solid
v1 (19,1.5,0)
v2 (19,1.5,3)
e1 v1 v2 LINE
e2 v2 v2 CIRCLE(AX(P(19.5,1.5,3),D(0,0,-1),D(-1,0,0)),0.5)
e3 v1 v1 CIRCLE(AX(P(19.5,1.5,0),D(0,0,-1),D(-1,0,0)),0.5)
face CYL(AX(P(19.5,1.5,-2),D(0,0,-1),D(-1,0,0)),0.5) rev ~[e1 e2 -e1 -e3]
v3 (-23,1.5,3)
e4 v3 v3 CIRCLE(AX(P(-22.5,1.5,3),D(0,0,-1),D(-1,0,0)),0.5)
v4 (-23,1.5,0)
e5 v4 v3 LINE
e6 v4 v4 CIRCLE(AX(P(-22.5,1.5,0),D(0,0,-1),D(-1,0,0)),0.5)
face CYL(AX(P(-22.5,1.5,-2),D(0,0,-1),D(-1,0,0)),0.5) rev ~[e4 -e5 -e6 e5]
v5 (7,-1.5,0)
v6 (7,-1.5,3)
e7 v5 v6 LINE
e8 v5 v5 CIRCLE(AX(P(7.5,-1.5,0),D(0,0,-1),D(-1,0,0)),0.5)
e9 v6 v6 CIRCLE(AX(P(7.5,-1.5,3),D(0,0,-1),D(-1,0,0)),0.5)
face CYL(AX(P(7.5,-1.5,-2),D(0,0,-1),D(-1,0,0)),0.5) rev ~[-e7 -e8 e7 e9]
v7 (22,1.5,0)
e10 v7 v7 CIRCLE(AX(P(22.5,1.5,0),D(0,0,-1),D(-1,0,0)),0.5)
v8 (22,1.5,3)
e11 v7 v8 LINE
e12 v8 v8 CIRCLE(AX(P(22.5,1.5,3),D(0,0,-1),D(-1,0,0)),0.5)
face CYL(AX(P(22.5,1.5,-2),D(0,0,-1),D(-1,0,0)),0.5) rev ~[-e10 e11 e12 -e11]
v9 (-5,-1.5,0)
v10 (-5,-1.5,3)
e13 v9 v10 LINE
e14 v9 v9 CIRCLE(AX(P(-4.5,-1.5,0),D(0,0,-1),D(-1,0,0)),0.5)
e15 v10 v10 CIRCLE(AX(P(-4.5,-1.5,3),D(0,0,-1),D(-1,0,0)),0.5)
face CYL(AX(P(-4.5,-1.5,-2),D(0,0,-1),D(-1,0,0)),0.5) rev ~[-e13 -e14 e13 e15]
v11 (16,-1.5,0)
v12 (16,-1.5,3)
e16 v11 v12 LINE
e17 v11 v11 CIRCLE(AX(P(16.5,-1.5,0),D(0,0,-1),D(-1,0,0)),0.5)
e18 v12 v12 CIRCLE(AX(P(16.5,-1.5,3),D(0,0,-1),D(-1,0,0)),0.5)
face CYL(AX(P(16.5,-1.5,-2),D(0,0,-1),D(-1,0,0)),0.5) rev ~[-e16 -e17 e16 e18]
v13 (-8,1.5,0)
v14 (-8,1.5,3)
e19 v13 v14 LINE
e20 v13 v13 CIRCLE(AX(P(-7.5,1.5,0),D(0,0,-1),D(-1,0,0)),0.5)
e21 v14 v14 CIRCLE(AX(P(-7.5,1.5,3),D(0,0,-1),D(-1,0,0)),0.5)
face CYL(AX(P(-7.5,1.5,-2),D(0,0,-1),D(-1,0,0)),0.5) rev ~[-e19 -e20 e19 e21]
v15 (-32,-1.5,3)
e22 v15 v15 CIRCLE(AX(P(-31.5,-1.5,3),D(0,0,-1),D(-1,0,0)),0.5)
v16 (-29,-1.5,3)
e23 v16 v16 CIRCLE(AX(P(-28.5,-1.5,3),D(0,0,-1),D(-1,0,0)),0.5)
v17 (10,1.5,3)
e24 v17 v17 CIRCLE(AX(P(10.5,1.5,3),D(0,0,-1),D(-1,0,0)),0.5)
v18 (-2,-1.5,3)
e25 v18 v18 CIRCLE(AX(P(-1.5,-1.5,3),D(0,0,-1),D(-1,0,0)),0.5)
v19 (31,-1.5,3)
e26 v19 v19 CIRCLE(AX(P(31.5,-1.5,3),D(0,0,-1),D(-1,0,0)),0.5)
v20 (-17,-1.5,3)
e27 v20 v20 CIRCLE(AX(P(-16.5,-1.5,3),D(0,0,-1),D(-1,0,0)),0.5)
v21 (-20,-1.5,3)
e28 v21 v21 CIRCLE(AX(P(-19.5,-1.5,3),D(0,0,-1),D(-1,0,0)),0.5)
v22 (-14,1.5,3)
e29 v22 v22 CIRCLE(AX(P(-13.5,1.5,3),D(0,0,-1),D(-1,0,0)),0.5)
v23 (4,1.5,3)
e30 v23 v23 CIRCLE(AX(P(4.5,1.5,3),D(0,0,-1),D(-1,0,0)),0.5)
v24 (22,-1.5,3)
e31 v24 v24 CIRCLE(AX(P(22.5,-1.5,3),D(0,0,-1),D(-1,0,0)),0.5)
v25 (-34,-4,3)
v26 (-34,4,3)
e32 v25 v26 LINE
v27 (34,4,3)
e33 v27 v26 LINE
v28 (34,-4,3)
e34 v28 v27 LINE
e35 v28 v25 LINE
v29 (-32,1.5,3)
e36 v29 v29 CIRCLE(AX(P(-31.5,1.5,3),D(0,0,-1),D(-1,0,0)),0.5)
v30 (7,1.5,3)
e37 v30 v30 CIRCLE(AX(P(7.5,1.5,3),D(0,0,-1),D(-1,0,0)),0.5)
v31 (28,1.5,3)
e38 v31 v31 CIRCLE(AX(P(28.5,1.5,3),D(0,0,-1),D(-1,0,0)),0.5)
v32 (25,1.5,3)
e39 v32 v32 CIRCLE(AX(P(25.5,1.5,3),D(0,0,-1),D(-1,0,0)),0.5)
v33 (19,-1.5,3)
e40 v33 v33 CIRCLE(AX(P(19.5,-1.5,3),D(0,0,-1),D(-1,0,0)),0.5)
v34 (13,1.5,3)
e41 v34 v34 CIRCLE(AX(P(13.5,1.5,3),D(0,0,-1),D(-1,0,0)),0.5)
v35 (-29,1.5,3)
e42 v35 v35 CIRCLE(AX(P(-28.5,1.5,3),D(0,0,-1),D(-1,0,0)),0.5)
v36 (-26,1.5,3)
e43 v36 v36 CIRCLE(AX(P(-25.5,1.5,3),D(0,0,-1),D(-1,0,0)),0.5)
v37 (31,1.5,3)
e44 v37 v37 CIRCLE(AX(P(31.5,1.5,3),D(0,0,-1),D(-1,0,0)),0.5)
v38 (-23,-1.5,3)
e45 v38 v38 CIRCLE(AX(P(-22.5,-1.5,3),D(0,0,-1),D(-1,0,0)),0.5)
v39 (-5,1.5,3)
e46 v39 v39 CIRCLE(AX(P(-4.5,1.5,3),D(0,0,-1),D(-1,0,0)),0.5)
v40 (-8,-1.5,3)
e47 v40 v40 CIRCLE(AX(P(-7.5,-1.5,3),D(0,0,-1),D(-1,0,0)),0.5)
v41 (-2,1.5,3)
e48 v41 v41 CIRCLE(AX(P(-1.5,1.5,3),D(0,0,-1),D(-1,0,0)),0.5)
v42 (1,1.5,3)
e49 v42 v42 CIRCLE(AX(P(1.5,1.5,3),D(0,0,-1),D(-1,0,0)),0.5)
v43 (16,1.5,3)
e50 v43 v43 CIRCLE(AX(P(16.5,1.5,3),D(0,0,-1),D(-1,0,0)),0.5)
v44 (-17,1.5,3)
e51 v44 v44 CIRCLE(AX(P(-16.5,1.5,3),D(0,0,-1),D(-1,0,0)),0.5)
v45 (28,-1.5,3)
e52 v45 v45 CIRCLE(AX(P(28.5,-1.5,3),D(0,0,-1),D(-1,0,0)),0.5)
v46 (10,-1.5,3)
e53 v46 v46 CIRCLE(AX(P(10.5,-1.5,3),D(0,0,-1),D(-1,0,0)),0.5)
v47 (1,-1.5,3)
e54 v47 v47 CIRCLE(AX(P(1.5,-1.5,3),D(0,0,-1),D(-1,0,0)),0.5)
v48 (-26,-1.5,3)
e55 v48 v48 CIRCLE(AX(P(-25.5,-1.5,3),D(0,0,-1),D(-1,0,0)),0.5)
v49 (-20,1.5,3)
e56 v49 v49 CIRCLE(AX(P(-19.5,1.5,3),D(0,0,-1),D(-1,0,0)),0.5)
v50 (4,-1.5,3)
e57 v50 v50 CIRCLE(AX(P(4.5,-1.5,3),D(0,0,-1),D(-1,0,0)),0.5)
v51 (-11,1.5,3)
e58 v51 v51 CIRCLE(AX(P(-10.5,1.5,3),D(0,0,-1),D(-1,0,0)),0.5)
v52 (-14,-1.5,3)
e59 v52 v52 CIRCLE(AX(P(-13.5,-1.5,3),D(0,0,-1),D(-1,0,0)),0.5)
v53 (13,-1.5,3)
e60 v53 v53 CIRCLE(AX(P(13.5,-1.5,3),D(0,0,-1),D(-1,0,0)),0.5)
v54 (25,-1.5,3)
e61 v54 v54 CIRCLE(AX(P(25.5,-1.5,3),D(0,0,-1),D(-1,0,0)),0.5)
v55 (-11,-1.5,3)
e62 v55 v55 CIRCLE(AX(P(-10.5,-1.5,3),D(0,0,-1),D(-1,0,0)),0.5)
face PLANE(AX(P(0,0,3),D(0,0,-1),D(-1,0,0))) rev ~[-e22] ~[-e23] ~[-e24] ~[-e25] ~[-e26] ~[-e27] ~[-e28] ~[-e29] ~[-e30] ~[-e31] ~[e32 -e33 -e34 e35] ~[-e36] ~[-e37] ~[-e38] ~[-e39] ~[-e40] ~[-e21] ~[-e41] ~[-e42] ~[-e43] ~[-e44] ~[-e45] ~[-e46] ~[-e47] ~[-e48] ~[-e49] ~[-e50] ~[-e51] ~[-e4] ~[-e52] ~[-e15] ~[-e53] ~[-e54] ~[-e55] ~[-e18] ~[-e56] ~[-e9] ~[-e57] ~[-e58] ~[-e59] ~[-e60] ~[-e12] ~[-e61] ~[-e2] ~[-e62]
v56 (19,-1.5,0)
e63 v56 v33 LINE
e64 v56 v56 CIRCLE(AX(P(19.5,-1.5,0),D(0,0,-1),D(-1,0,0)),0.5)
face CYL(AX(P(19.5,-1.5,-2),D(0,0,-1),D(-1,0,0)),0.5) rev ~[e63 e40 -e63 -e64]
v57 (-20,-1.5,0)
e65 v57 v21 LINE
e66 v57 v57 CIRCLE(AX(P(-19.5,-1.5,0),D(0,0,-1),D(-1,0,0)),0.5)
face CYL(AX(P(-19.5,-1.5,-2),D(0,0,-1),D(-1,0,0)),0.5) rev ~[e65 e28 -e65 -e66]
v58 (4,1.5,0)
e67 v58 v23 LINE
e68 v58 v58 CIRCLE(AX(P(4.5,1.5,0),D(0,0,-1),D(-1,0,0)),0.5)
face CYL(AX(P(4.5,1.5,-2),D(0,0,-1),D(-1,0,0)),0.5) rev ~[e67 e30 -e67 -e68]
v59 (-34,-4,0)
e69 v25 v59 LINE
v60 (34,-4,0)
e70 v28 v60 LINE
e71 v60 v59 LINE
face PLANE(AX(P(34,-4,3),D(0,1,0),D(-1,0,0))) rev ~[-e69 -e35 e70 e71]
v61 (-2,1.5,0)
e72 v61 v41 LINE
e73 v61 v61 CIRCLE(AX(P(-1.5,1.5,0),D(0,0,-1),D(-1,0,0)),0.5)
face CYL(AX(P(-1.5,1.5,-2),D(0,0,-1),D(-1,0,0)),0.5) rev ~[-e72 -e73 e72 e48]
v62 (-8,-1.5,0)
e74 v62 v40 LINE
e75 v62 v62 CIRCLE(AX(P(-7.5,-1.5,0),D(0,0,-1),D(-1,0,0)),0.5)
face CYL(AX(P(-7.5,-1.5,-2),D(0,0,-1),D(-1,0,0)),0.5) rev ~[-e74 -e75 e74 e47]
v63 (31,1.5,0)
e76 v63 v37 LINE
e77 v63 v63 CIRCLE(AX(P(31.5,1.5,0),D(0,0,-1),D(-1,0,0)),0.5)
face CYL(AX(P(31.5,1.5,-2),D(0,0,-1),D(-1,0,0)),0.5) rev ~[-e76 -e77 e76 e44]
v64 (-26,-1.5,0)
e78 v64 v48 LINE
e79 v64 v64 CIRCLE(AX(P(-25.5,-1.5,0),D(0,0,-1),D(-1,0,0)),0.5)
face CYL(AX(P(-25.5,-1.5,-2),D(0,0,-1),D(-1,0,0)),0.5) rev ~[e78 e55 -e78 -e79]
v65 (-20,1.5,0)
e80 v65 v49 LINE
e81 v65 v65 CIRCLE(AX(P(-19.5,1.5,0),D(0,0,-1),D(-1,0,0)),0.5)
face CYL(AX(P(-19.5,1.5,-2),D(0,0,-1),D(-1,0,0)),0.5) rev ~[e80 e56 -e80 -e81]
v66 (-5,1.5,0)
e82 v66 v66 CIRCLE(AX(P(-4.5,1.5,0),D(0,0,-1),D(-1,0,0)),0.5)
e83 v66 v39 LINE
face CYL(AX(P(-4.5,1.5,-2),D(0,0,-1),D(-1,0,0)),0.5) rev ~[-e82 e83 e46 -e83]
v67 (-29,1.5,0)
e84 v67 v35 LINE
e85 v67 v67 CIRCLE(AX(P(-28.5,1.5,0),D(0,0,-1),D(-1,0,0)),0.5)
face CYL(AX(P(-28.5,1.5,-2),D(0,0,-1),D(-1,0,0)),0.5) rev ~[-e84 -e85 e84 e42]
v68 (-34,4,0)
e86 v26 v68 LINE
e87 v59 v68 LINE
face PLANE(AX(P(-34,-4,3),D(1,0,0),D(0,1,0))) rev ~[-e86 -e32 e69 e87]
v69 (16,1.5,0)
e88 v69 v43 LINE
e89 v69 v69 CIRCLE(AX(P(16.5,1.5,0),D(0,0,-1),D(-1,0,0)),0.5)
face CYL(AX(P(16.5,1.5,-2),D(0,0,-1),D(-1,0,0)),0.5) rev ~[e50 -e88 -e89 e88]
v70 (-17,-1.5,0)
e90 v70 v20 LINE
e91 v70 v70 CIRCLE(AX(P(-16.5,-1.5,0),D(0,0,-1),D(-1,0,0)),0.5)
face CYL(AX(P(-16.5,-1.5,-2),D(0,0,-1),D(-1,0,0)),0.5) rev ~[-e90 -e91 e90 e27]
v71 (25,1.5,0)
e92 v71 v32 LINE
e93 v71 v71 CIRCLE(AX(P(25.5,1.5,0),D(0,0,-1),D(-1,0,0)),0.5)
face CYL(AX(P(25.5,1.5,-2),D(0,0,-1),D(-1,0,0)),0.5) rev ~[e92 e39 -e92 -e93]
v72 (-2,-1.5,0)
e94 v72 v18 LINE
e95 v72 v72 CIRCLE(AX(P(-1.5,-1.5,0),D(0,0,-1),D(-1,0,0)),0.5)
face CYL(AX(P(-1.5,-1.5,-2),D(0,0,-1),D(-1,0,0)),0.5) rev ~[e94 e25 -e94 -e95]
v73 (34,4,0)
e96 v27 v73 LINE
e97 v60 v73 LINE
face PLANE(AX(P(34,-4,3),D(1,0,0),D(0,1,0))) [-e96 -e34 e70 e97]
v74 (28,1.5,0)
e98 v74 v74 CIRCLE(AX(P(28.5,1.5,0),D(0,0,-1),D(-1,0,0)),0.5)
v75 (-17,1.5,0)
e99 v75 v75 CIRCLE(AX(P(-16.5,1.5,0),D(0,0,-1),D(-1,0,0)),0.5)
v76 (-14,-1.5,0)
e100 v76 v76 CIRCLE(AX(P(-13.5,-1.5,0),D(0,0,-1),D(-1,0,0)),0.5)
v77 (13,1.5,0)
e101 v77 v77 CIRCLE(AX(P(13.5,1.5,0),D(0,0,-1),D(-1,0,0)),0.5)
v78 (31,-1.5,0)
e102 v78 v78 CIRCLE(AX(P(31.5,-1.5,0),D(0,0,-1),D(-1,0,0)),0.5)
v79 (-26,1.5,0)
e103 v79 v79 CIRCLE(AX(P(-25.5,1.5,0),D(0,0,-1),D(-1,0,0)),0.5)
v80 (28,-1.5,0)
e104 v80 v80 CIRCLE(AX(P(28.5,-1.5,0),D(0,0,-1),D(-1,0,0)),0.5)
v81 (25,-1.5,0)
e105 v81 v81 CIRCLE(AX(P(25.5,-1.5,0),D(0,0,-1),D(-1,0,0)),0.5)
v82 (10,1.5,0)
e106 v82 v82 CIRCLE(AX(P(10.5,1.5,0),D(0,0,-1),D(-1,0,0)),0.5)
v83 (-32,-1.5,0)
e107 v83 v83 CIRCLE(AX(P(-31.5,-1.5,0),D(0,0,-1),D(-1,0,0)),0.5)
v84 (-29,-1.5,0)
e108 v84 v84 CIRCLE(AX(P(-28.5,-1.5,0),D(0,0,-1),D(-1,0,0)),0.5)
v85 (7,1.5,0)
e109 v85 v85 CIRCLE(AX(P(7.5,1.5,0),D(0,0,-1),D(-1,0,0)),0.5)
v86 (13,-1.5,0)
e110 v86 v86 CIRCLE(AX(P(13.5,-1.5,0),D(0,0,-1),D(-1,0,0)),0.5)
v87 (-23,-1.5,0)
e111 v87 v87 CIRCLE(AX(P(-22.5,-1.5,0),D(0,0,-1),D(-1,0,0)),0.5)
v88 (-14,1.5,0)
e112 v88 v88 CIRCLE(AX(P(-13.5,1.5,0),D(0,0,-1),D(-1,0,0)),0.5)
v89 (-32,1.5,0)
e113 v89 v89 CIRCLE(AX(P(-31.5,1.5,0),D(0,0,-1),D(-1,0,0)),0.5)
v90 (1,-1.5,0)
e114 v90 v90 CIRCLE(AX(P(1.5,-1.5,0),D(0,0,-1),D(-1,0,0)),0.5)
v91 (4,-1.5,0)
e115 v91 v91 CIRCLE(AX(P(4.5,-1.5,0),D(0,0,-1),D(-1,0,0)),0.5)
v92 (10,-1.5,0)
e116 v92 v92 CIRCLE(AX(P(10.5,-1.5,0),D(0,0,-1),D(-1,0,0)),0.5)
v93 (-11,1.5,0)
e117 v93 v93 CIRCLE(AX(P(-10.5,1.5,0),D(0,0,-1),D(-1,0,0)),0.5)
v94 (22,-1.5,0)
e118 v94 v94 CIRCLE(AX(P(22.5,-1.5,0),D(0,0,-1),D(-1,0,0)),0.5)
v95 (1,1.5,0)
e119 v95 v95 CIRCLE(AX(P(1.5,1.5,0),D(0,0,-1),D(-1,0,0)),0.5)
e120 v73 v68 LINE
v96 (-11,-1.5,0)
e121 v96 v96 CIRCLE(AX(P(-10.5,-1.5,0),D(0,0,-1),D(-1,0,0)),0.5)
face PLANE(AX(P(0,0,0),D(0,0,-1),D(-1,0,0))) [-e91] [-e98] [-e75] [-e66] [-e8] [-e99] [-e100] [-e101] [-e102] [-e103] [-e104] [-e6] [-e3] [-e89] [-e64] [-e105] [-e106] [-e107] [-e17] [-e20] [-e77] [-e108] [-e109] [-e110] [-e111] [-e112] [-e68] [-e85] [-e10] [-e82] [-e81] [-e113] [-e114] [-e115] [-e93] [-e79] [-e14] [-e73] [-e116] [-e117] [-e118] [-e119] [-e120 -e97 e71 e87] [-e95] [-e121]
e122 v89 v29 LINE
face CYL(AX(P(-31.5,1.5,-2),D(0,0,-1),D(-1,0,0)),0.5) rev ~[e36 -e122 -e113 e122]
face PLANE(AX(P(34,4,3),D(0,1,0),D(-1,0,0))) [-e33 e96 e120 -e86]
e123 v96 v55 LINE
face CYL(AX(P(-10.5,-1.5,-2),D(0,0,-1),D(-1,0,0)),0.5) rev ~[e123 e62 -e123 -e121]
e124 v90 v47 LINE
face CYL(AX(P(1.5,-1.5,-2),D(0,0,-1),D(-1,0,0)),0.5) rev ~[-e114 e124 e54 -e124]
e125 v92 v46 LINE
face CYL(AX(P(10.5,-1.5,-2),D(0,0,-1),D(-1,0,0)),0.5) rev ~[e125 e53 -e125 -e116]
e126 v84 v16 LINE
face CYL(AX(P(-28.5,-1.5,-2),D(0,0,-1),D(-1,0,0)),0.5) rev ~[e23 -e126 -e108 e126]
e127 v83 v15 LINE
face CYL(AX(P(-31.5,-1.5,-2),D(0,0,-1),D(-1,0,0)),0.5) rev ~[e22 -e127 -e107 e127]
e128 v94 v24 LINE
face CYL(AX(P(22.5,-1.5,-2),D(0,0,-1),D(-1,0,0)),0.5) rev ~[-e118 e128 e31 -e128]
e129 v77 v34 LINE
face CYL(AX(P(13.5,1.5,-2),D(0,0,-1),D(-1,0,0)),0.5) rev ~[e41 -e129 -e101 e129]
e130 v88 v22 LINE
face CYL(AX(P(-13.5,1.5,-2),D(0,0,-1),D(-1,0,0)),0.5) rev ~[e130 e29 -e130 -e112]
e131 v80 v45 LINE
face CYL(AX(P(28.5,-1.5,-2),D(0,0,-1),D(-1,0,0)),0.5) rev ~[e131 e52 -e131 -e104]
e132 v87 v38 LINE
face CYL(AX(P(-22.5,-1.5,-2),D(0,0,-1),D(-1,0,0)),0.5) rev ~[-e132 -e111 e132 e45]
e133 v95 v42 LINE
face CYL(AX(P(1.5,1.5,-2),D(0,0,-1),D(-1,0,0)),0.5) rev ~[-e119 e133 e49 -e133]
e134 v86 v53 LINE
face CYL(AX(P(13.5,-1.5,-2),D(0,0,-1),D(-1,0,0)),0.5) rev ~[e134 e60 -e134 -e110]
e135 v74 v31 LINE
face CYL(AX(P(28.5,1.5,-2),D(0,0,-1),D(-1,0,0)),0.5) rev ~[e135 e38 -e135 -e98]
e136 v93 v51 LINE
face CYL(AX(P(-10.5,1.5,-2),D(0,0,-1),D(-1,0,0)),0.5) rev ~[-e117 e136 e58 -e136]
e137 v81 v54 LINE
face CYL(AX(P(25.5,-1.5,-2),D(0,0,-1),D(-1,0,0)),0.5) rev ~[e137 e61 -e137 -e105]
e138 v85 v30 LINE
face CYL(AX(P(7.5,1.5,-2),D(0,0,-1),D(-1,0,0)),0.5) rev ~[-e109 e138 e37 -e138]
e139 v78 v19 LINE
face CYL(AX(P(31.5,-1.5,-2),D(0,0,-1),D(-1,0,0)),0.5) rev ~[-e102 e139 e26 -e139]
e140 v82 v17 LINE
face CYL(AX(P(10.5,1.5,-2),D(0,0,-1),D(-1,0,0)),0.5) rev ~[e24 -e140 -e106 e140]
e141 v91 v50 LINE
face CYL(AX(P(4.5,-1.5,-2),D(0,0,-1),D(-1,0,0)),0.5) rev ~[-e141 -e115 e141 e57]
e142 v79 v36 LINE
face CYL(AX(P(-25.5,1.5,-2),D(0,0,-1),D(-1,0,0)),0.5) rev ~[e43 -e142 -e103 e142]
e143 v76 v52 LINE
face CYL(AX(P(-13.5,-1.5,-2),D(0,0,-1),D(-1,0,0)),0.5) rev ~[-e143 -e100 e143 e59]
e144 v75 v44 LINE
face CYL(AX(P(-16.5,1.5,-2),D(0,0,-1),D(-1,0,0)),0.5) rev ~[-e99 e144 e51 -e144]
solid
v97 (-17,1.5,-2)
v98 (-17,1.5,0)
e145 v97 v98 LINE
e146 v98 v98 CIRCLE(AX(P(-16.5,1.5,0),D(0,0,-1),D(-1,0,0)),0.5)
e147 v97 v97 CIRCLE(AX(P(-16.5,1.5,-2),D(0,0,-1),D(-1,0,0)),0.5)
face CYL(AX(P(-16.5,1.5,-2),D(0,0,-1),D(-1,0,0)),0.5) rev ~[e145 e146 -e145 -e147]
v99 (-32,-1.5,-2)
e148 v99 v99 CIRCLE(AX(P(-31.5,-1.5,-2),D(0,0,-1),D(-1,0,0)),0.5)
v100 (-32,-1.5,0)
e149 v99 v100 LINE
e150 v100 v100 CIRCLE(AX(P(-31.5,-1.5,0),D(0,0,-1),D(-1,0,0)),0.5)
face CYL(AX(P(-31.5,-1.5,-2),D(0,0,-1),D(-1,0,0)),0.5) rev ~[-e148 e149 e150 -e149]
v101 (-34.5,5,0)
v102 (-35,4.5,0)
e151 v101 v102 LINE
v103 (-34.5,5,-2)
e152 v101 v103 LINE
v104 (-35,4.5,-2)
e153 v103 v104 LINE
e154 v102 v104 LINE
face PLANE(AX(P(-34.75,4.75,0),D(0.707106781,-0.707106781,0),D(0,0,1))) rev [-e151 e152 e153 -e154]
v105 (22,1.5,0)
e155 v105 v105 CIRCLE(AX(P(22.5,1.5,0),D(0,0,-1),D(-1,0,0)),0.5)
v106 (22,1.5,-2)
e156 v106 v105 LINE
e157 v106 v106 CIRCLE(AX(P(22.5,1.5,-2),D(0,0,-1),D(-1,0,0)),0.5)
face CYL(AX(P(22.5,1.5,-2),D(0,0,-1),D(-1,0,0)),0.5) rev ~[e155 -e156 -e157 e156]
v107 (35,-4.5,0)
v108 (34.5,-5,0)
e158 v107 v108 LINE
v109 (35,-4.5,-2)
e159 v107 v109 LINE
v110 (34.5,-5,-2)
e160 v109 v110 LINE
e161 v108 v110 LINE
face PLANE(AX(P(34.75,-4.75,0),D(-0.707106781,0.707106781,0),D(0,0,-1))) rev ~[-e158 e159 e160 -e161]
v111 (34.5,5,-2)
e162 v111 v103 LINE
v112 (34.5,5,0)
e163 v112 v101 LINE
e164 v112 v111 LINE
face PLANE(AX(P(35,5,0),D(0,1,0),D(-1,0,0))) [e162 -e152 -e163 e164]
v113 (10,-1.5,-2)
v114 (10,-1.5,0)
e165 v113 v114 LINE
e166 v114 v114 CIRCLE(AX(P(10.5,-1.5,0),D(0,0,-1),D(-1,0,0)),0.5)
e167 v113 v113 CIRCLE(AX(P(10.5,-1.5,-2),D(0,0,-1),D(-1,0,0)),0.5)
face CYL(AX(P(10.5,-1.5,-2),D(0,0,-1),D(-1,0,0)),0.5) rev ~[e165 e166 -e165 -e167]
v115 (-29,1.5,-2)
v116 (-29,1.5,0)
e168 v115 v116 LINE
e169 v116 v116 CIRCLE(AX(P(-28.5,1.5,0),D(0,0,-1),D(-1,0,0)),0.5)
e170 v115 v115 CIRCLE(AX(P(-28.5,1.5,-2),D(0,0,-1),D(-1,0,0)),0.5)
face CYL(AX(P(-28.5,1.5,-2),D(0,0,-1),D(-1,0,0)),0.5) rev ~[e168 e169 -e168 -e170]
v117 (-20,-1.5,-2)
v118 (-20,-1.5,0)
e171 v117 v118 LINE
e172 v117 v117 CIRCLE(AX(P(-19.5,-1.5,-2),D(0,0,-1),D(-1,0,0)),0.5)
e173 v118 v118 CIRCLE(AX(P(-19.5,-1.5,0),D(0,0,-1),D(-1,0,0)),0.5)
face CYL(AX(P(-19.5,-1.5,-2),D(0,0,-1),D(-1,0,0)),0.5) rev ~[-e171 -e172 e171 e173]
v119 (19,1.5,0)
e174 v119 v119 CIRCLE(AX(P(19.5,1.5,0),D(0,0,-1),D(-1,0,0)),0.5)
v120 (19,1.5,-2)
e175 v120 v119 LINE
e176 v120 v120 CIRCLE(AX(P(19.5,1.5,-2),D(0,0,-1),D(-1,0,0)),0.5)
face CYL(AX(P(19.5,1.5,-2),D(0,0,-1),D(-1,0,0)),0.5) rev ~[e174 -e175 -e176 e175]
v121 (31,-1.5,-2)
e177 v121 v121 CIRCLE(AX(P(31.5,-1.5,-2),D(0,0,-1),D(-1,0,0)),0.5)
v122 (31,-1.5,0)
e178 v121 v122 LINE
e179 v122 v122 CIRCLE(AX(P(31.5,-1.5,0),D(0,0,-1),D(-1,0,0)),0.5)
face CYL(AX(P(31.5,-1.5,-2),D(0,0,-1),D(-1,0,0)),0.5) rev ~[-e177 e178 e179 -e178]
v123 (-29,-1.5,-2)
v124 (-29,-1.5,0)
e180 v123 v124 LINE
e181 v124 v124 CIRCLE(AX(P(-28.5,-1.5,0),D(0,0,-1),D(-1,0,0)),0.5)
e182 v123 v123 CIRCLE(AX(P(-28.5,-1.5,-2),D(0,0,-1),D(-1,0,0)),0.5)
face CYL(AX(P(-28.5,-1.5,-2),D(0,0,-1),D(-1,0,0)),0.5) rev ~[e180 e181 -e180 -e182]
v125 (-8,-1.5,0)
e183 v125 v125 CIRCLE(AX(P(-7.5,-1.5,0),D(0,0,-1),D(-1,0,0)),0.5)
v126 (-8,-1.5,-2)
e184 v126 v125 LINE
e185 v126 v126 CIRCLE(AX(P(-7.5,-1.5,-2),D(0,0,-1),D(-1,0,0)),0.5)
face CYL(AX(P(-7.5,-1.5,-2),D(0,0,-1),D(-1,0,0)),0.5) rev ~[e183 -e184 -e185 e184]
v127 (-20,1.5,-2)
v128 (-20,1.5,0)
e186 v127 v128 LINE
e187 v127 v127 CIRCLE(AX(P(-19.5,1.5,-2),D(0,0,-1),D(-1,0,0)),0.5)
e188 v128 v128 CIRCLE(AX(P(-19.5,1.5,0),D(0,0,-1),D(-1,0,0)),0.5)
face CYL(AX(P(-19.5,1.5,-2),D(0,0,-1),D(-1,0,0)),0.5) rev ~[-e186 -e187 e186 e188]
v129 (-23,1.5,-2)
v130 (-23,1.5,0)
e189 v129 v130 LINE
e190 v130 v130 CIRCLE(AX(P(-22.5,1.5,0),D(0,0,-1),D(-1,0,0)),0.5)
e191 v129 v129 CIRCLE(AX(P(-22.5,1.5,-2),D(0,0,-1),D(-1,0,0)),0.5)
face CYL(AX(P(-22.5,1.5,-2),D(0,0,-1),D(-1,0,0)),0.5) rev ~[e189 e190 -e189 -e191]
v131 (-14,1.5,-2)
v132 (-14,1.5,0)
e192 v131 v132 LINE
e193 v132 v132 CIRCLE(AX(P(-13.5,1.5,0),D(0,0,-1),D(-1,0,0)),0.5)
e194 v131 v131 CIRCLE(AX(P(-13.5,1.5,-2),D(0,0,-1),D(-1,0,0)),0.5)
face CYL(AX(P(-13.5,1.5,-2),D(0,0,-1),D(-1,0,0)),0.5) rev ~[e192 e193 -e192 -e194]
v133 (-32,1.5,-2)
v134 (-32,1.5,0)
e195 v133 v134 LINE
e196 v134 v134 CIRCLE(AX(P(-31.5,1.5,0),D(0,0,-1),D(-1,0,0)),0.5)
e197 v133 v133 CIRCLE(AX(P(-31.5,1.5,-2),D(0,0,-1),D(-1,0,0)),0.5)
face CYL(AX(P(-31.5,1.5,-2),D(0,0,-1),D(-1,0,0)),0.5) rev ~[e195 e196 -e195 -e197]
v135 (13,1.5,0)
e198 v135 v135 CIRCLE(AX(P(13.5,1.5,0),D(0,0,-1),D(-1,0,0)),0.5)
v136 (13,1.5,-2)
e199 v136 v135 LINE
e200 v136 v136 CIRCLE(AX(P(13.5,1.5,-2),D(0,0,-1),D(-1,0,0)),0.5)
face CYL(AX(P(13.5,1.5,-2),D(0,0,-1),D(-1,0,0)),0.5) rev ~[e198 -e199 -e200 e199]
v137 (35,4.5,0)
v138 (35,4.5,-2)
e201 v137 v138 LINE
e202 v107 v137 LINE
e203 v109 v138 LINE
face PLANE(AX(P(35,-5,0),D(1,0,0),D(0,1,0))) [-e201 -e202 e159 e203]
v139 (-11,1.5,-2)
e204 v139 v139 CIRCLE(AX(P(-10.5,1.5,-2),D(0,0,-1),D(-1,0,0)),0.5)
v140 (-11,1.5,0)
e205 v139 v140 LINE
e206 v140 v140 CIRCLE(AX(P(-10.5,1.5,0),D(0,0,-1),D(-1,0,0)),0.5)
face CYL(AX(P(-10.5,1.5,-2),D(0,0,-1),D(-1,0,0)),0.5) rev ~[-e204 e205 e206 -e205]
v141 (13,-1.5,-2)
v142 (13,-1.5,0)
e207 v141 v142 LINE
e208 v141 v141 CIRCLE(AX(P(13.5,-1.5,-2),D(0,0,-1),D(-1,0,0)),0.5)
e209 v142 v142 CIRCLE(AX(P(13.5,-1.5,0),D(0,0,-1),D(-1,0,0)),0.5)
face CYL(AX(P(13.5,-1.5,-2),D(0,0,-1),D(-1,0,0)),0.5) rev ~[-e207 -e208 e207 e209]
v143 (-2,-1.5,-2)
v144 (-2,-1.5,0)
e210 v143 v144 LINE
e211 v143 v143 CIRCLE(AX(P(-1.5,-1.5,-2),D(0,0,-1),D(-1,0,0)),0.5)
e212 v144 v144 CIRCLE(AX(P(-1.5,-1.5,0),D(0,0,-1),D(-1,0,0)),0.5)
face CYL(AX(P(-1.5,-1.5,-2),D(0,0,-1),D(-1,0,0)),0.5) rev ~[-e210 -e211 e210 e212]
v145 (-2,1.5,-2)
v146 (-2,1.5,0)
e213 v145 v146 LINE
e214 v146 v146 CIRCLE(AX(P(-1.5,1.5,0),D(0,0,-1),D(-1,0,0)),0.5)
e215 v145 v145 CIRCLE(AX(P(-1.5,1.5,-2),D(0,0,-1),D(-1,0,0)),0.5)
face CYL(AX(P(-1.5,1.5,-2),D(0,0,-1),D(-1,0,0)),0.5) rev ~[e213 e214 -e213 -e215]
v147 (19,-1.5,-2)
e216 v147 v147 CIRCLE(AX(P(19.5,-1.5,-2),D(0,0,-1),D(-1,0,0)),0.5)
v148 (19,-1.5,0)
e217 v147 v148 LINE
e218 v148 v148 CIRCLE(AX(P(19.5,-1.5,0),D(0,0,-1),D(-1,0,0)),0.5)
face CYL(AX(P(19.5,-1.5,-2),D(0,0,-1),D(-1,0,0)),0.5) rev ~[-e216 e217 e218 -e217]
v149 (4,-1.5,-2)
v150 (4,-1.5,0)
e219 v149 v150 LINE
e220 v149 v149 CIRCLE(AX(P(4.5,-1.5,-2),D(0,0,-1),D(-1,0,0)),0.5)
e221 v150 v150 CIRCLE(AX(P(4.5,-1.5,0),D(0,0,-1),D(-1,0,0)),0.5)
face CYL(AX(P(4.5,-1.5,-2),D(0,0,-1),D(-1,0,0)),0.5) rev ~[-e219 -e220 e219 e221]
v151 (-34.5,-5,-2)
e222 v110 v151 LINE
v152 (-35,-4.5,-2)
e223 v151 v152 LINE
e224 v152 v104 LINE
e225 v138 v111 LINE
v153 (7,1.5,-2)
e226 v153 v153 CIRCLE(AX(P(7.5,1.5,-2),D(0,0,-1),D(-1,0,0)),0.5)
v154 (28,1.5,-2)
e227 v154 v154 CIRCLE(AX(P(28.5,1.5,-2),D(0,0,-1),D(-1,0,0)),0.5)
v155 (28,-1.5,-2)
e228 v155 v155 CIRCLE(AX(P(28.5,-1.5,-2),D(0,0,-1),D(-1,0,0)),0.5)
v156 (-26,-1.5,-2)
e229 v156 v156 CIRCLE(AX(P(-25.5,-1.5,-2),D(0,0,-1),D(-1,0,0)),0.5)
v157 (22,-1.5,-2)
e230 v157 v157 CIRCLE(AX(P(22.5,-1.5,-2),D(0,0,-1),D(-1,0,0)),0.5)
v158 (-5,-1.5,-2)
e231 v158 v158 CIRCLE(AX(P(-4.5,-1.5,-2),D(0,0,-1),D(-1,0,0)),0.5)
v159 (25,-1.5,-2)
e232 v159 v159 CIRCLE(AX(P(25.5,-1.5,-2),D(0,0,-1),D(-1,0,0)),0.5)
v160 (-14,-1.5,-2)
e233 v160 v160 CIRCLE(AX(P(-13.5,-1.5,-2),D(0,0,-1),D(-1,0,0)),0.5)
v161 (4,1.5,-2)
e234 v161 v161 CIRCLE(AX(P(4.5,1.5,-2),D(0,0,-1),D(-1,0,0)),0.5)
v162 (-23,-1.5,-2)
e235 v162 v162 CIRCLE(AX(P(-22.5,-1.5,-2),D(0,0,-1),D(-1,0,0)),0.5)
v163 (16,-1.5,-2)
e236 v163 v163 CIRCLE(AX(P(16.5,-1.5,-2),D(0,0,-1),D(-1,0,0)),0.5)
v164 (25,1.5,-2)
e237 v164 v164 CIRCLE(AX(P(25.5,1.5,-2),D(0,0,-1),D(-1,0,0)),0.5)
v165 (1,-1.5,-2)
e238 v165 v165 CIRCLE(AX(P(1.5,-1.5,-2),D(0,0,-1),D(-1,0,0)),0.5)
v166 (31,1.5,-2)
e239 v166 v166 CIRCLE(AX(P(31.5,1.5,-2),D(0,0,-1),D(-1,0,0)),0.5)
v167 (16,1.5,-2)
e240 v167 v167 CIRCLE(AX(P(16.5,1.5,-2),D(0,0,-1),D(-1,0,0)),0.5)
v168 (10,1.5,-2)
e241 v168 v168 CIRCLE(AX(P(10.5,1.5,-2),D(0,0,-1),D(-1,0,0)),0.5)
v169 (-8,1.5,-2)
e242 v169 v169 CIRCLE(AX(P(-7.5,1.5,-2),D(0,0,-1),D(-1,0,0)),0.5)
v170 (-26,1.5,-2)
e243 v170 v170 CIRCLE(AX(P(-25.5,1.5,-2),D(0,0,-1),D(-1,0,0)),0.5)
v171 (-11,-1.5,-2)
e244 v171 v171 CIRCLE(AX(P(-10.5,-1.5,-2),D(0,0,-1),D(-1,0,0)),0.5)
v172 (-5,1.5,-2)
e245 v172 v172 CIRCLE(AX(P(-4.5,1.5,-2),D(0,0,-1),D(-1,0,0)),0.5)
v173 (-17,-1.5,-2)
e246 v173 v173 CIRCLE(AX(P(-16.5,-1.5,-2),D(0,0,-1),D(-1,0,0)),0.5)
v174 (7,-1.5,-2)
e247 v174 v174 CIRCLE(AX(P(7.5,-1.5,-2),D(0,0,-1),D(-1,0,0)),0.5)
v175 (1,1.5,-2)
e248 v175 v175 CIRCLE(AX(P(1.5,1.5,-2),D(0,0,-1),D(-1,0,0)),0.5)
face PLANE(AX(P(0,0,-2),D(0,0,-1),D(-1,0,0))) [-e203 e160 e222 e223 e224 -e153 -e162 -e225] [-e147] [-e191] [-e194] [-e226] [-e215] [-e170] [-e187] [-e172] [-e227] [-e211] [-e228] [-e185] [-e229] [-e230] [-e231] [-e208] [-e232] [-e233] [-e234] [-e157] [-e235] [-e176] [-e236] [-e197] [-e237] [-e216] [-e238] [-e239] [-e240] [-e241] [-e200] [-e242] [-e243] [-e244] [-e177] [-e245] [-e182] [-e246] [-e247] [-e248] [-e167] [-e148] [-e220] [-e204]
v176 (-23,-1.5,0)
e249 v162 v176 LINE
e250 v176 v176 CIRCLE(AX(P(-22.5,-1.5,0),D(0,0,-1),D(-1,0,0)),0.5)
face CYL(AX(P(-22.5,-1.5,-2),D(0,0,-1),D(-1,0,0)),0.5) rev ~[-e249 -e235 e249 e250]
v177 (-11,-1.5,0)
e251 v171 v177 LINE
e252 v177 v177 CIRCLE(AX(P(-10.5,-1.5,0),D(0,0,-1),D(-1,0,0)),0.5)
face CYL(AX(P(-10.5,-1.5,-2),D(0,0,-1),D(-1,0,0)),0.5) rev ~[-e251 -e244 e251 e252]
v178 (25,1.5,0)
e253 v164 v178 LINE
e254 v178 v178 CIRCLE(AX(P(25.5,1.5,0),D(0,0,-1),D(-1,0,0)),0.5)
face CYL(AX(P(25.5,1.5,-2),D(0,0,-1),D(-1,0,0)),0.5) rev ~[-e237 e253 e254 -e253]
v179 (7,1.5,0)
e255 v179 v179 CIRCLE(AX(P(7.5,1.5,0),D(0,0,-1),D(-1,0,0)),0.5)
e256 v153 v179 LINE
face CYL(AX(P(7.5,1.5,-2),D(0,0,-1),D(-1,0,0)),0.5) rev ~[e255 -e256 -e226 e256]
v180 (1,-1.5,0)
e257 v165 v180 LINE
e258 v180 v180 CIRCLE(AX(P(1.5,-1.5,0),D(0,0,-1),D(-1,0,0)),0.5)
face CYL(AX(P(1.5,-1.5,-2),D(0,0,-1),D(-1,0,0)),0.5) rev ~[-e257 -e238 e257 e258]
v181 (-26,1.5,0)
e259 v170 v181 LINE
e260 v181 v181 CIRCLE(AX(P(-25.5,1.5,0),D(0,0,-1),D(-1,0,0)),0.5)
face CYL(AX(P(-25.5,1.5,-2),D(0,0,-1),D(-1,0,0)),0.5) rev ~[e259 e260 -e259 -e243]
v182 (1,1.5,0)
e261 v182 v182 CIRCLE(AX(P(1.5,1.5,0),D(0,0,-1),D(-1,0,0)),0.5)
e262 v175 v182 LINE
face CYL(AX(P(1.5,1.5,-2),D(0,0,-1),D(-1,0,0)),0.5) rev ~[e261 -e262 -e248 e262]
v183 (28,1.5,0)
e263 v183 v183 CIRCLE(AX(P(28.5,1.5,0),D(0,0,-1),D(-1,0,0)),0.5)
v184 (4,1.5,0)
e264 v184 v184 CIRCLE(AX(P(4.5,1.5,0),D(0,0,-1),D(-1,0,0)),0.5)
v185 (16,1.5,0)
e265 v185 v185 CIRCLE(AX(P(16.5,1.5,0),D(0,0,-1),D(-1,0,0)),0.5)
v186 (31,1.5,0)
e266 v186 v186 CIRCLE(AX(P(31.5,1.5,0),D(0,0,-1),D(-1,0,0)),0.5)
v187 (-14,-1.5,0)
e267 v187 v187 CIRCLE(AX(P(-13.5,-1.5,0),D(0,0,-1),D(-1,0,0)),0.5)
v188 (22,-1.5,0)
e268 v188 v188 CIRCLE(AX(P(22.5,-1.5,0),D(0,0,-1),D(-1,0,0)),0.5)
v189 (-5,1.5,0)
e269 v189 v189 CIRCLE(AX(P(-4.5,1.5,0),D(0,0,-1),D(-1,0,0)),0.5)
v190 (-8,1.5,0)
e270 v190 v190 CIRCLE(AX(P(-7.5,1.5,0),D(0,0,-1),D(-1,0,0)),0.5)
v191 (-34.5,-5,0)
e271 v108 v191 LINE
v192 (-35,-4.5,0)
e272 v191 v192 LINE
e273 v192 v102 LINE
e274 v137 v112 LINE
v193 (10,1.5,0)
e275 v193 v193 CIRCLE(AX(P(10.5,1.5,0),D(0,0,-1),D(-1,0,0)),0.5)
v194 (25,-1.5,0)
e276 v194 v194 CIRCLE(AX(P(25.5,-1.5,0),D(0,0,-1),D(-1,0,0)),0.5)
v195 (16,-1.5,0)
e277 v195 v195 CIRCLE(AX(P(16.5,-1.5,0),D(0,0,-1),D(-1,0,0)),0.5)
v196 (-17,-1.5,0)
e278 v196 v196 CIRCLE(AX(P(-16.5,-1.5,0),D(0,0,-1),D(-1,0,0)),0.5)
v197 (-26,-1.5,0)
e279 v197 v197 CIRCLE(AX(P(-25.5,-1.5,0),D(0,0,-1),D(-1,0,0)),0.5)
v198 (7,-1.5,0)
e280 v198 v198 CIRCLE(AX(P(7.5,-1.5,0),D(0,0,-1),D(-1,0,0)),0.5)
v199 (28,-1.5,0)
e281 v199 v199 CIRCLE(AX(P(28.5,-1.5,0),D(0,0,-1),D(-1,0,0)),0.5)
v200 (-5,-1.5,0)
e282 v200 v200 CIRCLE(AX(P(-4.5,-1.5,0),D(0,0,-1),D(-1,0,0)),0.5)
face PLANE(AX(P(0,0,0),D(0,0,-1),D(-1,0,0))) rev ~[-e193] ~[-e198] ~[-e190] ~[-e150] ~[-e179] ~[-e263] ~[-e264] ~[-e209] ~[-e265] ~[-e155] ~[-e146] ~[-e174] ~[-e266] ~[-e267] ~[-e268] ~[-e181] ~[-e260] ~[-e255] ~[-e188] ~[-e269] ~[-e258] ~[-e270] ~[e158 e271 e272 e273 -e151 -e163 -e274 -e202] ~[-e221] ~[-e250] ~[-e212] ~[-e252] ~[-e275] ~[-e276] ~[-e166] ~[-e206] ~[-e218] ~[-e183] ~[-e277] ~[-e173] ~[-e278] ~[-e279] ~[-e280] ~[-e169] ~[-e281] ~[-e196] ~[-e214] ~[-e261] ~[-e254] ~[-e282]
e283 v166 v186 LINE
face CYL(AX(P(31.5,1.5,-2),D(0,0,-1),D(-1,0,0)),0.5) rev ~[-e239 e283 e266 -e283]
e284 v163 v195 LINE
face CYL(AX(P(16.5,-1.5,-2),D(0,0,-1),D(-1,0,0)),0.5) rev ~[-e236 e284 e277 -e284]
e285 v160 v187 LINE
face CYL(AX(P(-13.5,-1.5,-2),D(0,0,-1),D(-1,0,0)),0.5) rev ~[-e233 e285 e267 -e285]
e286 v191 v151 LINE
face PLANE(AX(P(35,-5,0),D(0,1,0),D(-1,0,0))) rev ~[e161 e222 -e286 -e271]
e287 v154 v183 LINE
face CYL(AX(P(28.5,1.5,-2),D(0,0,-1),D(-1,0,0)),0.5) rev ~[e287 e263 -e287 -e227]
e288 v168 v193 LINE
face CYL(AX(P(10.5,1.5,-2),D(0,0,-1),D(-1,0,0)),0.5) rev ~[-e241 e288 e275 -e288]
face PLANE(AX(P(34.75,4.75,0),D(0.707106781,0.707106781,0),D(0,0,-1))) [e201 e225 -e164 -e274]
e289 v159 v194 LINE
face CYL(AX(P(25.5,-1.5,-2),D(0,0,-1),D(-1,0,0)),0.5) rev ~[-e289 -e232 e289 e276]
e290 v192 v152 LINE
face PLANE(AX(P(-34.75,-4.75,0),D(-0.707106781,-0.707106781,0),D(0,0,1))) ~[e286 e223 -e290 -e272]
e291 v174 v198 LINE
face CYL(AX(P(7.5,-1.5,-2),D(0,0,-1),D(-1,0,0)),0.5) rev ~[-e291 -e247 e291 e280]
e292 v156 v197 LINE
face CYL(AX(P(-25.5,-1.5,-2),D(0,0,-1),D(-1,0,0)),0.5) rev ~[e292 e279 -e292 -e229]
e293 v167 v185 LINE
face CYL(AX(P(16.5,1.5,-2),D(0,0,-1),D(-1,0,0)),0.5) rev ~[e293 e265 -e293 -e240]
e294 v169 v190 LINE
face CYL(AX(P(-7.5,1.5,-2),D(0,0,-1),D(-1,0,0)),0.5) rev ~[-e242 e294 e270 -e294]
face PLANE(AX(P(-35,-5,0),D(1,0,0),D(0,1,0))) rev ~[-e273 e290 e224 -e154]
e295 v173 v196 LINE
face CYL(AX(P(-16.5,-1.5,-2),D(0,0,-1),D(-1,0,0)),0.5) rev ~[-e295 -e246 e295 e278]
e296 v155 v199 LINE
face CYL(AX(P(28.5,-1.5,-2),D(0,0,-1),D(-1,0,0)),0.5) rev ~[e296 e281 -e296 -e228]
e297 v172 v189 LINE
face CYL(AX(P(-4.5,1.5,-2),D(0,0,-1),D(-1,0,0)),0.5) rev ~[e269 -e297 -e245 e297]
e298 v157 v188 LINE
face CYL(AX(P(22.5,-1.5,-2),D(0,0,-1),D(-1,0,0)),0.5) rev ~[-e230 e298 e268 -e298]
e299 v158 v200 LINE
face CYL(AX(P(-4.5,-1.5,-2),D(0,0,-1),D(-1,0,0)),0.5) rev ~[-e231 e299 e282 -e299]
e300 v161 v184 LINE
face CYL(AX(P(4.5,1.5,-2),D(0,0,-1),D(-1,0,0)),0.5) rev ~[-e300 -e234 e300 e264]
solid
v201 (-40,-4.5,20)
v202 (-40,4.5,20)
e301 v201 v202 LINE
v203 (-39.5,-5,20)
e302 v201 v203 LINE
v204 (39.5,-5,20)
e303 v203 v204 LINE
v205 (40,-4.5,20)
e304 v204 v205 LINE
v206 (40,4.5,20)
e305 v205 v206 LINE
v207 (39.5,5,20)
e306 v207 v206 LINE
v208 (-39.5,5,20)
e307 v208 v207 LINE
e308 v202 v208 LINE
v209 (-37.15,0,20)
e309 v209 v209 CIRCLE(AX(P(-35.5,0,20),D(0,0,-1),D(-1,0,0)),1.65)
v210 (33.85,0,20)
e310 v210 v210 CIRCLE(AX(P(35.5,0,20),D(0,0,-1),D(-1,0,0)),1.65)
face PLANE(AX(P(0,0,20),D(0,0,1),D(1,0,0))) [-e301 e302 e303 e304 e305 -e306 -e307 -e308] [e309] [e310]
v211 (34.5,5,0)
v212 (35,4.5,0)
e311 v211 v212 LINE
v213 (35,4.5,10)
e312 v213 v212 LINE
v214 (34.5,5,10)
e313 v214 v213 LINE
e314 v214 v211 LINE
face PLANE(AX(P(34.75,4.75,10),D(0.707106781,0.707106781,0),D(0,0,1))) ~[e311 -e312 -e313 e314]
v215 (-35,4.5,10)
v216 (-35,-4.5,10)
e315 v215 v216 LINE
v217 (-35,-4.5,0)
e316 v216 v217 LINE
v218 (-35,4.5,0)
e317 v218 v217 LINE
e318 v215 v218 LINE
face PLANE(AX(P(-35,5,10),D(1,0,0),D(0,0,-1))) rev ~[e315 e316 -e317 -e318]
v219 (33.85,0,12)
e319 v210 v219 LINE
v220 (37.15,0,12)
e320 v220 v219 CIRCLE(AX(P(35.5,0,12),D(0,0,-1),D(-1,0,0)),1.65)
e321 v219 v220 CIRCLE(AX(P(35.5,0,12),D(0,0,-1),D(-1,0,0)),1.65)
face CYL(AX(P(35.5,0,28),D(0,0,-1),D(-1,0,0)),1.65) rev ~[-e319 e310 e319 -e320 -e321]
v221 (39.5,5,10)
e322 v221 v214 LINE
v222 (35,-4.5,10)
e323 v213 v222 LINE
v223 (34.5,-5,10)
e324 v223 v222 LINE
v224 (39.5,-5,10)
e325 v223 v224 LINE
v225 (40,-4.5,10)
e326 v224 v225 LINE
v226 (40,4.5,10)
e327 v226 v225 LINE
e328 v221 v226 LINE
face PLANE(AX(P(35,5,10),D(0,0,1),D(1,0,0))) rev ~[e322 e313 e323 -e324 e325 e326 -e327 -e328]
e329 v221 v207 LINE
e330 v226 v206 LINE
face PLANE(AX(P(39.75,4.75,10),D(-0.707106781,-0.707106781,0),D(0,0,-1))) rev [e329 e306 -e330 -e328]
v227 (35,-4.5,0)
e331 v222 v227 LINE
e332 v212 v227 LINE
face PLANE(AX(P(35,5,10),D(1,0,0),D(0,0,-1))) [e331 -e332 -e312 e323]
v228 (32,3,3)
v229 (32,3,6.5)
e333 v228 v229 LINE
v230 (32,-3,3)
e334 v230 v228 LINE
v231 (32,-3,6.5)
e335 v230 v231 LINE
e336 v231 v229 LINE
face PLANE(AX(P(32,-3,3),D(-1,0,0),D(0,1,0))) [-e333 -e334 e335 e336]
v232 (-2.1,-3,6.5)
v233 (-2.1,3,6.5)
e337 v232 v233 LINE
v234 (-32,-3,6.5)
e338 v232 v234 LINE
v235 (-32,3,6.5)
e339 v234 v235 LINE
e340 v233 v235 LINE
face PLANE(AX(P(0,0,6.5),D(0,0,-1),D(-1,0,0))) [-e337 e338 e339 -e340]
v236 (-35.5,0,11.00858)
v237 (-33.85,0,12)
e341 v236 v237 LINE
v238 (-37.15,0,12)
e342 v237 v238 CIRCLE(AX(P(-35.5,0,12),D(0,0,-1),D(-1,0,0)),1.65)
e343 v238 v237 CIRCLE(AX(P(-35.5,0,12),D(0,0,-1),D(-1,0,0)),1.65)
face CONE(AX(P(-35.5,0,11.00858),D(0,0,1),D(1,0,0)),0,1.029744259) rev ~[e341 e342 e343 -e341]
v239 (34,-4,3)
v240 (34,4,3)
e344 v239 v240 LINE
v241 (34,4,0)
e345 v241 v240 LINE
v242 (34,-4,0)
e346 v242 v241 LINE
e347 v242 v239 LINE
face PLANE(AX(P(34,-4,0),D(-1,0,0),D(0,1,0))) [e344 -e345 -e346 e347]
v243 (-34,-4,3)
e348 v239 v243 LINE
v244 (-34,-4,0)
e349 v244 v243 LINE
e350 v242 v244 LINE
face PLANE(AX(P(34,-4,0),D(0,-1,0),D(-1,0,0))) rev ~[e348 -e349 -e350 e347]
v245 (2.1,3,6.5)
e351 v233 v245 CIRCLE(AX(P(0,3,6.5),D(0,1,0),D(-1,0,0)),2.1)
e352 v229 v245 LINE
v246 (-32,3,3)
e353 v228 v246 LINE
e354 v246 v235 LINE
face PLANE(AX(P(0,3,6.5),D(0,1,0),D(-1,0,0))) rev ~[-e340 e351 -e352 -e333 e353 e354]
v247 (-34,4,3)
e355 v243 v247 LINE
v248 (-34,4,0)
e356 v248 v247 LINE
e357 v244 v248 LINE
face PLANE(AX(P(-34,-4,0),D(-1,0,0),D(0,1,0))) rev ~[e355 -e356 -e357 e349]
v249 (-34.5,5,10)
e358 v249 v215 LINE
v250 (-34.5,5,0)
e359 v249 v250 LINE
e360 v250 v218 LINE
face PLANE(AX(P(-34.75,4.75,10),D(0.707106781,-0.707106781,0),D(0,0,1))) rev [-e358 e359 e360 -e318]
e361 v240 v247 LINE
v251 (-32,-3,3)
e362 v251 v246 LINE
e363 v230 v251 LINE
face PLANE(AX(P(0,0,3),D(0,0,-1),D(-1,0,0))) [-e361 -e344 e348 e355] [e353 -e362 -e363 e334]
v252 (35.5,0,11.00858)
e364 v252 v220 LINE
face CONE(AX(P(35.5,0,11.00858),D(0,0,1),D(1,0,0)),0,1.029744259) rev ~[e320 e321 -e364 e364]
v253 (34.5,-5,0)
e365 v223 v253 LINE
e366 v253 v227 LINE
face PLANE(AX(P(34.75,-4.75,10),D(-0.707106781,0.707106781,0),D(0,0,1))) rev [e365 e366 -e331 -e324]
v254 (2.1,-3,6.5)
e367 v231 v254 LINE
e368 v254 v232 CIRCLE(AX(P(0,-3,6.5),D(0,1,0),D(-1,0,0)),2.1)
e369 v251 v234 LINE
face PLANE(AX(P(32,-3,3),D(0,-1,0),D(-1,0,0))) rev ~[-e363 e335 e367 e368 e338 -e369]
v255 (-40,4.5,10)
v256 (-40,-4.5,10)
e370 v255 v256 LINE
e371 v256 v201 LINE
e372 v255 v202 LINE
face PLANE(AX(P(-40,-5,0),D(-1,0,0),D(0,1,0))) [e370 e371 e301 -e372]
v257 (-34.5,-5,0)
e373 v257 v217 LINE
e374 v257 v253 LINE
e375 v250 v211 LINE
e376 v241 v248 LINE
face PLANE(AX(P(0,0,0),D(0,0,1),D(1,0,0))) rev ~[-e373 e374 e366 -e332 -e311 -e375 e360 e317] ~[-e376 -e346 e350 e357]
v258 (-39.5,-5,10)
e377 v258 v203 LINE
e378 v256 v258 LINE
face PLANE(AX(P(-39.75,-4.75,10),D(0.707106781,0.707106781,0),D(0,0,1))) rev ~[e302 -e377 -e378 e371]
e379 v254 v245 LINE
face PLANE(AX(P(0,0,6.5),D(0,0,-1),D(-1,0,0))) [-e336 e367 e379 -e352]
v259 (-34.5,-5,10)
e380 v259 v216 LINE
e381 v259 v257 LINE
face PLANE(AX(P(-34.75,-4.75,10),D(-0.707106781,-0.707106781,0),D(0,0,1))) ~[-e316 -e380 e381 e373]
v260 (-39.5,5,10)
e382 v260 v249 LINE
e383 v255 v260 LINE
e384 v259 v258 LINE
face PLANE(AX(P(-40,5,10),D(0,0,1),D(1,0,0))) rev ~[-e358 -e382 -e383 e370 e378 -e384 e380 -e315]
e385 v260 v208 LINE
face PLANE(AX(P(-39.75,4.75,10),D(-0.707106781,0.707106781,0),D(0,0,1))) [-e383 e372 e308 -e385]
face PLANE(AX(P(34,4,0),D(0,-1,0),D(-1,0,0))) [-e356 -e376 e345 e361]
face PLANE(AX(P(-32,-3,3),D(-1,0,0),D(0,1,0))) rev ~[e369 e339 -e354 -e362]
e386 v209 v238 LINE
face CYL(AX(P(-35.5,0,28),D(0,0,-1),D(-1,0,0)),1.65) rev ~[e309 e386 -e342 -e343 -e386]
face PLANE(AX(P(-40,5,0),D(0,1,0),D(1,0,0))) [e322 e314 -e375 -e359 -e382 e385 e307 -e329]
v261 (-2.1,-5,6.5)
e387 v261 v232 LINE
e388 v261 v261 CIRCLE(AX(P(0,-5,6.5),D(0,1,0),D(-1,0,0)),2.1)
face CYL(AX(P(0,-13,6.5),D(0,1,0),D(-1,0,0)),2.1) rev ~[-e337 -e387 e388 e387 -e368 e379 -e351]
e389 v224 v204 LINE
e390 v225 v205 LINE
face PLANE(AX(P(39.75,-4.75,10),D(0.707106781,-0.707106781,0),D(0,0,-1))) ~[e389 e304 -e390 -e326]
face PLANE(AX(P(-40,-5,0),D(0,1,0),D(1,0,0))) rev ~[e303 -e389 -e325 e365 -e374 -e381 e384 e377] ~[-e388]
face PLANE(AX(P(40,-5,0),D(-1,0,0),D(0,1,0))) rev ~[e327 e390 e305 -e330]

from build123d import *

# Parameters (mm, degrees)
SKETCH1_W             = 80
SKETCH1_H             = 10
BOSS_EXTRUDE1_DEPTH   = 20
SKETCH9_W             = 5
SKETCH9_H             = 10
CUT_EXTRUDE3_DEPTH    = 46.82575695
M4_TAPPED_HOLE1_D     = 3.3
M4_TAPPED_HOLE1_DEPTH = 8
M4_TAPPED_HOLE1_TIP   = 0.991420021
M5_TAPPED_HOLE1_D     = 4.2
M5_TAPPED_HOLE1_DEPTH = 8
SKETCH8_W             = 68
SKETCH8_H             = 8
CUT_EXTRUDE2_DEPTH    = 3
SKETCH10_W            = 64
SKETCH10_H            = 6
CUT_EXTRUDE4_DEPTH    = 3.5
SKETCH11_W            = 68
SKETCH11_H            = 8
BOSS_EXTRUDE2_DEPTH   = 3
SKETCH12_W            = 70
SKETCH12_H            = 10
BOSS_EXTRUDE3_DEPTH   = 2
SKETCH13_R            = 0.5
CUT_EXTRUDE5_DEPTH    = 5
LPATTERN1_COUNT       = 22
LPATTERN1_PITCH       = 3
CHAMFER1_SIZE         = 0.5
CHAMFER2_SIZE         = 0.5


with BuildPart() as part:
    # Sketch1 → Boss-Extrude1 (new body)
    with BuildSketch(Plane.XY):
        Rectangle(SKETCH1_W, SKETCH1_H)
    extrude(amount=BOSS_EXTRUDE1_DEPTH)

    # Sketch9 → Cut-Extrude3 (cut, through all)
    with BuildSketch(Plane(origin=(0, 5, 0), x_dir=(1, 0, 0), z_dir=(0, 1, 0))):
        with Locations((37.5, -5)):
            Rectangle(SKETCH9_W, SKETCH9_H)
        with Locations((-37.5, -5)):
            Rectangle(SKETCH9_W, SKETCH9_H)
    extrude(amount=-CUT_EXTRUDE3_DEPTH, mode=Mode.SUBTRACT)

    # M4 Tapped Hole1
    with Locations(Plane.XY.offset(20)):
        with Locations((-35.5, 0), (35.5, 0)):
            Hole(M4_TAPPED_HOLE1_D / 2, depth=M4_TAPPED_HOLE1_DEPTH)
            with Locations((0, 0, -(M4_TAPPED_HOLE1_DEPTH + M4_TAPPED_HOLE1_TIP / 2))):  # 118° drill point
                Cone(0, M4_TAPPED_HOLE1_D / 2, M4_TAPPED_HOLE1_TIP, mode=Mode.SUBTRACT)

    # M5 Tapped Hole1
    with Locations(Plane.XZ.offset(5)):
        with Locations((0, 6.5)):
            Hole(M5_TAPPED_HOLE1_D / 2, depth=M5_TAPPED_HOLE1_DEPTH)

    # Sketch8 → Cut-Extrude2 (cut)
    with BuildSketch(Plane(origin=(0, 0, 0), x_dir=(-1, 0, 0), z_dir=(0, 0, -1))):
        Rectangle(SKETCH8_W, SKETCH8_H)
    extrude(amount=-CUT_EXTRUDE2_DEPTH, mode=Mode.SUBTRACT)

    # Sketch10 → Cut-Extrude4 (cut)
    with BuildSketch(Plane(origin=(0, 0, 3), x_dir=(-1, 0, 0), z_dir=(0, 0, -1))):
        Rectangle(SKETCH10_W, SKETCH10_H)
    extrude(amount=-CUT_EXTRUDE4_DEPTH, mode=Mode.SUBTRACT)

    # Chamfer1
    chamfer1_edges = [part.edges().sort_by_distance(p)[0] for p in [
        (35, -5, 5),
        (35, 5, 5),
        (-35, -5, 5),
        (-35, 5, 5),
        (-40, 5, 15),
        (40, 5, 15),
        (40, -5, 15),
        (-40, -5, 15),
    ]]
    chamfer(chamfer1_edges, length=CHAMFER1_SIZE)


with BuildPart() as body_2:
    # Sketch11 → Boss-Extrude2 (new body)
    with BuildSketch(Plane(origin=(0, 0, 3), x_dir=(-1, 0, 0), z_dir=(0, 0, -1))):
        Rectangle(SKETCH11_W, SKETCH11_H)
    extrude(amount=BOSS_EXTRUDE2_DEPTH)


with BuildPart() as body_3:
    # Sketch12 → Boss-Extrude3 (new body)
    with BuildSketch(Plane(origin=(0, 0, 0), x_dir=(-1, 0, 0), z_dir=(0, 0, -1))):
        Rectangle(SKETCH12_W, SKETCH12_H)
    extrude(amount=BOSS_EXTRUDE3_DEPTH)


with BuildPart() as cut_extrude5_tool:
    # Sketch13 → Cut-Extrude5 (new body)
    with BuildSketch(Plane(origin=(0, 0, -2), x_dir=(-1, 0, 0), z_dir=(0, 0, -1))):
        with Locations((31.5, 1.5)):
            Circle(SKETCH13_R)
        with Locations((31.5, -1.5)):
            Circle(SKETCH13_R)
    cut_extrude5 = extrude(amount=-CUT_EXTRUDE5_DEPTH)


with BuildPart() as body_2_1:
    add(body_2.part)

    # Cut-Extrude5: cut by cut_extrude5_tool
    add(cut_extrude5_tool.part, mode=Mode.SUBTRACT)


with BuildPart() as body_3_1:
    add(body_3.part)

    # Cut-Extrude5: cut by cut_extrude5_tool
    add(cut_extrude5_tool.part, mode=Mode.SUBTRACT)


with BuildPart() as lpattern1_tool:
    # LPattern1: Cut-Extrude5 ×22
    with Locations(*[(i * LPATTERN1_PITCH, 0, 0) for i in range(1, LPATTERN1_COUNT)]):
        add(cut_extrude5)


with BuildPart() as body_2_2:
    add(body_2_1.part)

    # LPattern1: cut by lpattern1_tool
    add(lpattern1_tool.part, mode=Mode.SUBTRACT)


with BuildPart() as body_3_2:
    add(body_3_1.part)

    # LPattern1: cut by lpattern1_tool
    add(lpattern1_tool.part, mode=Mode.SUBTRACT)

    # Chamfer2
    chamfer2_edges = [body_3_2.edges().sort_by_distance(p)[0] for p in [
        (35, 5, -1),
        (-35, 5, -1),
        (-35, -5, -1),
        (35, -5, -1),
    ]]
    chamfer(chamfer2_edges, length=CHAMFER2_SIZE)


solid = Compound([part.part, body_2_2.part, body_3_2.part])
